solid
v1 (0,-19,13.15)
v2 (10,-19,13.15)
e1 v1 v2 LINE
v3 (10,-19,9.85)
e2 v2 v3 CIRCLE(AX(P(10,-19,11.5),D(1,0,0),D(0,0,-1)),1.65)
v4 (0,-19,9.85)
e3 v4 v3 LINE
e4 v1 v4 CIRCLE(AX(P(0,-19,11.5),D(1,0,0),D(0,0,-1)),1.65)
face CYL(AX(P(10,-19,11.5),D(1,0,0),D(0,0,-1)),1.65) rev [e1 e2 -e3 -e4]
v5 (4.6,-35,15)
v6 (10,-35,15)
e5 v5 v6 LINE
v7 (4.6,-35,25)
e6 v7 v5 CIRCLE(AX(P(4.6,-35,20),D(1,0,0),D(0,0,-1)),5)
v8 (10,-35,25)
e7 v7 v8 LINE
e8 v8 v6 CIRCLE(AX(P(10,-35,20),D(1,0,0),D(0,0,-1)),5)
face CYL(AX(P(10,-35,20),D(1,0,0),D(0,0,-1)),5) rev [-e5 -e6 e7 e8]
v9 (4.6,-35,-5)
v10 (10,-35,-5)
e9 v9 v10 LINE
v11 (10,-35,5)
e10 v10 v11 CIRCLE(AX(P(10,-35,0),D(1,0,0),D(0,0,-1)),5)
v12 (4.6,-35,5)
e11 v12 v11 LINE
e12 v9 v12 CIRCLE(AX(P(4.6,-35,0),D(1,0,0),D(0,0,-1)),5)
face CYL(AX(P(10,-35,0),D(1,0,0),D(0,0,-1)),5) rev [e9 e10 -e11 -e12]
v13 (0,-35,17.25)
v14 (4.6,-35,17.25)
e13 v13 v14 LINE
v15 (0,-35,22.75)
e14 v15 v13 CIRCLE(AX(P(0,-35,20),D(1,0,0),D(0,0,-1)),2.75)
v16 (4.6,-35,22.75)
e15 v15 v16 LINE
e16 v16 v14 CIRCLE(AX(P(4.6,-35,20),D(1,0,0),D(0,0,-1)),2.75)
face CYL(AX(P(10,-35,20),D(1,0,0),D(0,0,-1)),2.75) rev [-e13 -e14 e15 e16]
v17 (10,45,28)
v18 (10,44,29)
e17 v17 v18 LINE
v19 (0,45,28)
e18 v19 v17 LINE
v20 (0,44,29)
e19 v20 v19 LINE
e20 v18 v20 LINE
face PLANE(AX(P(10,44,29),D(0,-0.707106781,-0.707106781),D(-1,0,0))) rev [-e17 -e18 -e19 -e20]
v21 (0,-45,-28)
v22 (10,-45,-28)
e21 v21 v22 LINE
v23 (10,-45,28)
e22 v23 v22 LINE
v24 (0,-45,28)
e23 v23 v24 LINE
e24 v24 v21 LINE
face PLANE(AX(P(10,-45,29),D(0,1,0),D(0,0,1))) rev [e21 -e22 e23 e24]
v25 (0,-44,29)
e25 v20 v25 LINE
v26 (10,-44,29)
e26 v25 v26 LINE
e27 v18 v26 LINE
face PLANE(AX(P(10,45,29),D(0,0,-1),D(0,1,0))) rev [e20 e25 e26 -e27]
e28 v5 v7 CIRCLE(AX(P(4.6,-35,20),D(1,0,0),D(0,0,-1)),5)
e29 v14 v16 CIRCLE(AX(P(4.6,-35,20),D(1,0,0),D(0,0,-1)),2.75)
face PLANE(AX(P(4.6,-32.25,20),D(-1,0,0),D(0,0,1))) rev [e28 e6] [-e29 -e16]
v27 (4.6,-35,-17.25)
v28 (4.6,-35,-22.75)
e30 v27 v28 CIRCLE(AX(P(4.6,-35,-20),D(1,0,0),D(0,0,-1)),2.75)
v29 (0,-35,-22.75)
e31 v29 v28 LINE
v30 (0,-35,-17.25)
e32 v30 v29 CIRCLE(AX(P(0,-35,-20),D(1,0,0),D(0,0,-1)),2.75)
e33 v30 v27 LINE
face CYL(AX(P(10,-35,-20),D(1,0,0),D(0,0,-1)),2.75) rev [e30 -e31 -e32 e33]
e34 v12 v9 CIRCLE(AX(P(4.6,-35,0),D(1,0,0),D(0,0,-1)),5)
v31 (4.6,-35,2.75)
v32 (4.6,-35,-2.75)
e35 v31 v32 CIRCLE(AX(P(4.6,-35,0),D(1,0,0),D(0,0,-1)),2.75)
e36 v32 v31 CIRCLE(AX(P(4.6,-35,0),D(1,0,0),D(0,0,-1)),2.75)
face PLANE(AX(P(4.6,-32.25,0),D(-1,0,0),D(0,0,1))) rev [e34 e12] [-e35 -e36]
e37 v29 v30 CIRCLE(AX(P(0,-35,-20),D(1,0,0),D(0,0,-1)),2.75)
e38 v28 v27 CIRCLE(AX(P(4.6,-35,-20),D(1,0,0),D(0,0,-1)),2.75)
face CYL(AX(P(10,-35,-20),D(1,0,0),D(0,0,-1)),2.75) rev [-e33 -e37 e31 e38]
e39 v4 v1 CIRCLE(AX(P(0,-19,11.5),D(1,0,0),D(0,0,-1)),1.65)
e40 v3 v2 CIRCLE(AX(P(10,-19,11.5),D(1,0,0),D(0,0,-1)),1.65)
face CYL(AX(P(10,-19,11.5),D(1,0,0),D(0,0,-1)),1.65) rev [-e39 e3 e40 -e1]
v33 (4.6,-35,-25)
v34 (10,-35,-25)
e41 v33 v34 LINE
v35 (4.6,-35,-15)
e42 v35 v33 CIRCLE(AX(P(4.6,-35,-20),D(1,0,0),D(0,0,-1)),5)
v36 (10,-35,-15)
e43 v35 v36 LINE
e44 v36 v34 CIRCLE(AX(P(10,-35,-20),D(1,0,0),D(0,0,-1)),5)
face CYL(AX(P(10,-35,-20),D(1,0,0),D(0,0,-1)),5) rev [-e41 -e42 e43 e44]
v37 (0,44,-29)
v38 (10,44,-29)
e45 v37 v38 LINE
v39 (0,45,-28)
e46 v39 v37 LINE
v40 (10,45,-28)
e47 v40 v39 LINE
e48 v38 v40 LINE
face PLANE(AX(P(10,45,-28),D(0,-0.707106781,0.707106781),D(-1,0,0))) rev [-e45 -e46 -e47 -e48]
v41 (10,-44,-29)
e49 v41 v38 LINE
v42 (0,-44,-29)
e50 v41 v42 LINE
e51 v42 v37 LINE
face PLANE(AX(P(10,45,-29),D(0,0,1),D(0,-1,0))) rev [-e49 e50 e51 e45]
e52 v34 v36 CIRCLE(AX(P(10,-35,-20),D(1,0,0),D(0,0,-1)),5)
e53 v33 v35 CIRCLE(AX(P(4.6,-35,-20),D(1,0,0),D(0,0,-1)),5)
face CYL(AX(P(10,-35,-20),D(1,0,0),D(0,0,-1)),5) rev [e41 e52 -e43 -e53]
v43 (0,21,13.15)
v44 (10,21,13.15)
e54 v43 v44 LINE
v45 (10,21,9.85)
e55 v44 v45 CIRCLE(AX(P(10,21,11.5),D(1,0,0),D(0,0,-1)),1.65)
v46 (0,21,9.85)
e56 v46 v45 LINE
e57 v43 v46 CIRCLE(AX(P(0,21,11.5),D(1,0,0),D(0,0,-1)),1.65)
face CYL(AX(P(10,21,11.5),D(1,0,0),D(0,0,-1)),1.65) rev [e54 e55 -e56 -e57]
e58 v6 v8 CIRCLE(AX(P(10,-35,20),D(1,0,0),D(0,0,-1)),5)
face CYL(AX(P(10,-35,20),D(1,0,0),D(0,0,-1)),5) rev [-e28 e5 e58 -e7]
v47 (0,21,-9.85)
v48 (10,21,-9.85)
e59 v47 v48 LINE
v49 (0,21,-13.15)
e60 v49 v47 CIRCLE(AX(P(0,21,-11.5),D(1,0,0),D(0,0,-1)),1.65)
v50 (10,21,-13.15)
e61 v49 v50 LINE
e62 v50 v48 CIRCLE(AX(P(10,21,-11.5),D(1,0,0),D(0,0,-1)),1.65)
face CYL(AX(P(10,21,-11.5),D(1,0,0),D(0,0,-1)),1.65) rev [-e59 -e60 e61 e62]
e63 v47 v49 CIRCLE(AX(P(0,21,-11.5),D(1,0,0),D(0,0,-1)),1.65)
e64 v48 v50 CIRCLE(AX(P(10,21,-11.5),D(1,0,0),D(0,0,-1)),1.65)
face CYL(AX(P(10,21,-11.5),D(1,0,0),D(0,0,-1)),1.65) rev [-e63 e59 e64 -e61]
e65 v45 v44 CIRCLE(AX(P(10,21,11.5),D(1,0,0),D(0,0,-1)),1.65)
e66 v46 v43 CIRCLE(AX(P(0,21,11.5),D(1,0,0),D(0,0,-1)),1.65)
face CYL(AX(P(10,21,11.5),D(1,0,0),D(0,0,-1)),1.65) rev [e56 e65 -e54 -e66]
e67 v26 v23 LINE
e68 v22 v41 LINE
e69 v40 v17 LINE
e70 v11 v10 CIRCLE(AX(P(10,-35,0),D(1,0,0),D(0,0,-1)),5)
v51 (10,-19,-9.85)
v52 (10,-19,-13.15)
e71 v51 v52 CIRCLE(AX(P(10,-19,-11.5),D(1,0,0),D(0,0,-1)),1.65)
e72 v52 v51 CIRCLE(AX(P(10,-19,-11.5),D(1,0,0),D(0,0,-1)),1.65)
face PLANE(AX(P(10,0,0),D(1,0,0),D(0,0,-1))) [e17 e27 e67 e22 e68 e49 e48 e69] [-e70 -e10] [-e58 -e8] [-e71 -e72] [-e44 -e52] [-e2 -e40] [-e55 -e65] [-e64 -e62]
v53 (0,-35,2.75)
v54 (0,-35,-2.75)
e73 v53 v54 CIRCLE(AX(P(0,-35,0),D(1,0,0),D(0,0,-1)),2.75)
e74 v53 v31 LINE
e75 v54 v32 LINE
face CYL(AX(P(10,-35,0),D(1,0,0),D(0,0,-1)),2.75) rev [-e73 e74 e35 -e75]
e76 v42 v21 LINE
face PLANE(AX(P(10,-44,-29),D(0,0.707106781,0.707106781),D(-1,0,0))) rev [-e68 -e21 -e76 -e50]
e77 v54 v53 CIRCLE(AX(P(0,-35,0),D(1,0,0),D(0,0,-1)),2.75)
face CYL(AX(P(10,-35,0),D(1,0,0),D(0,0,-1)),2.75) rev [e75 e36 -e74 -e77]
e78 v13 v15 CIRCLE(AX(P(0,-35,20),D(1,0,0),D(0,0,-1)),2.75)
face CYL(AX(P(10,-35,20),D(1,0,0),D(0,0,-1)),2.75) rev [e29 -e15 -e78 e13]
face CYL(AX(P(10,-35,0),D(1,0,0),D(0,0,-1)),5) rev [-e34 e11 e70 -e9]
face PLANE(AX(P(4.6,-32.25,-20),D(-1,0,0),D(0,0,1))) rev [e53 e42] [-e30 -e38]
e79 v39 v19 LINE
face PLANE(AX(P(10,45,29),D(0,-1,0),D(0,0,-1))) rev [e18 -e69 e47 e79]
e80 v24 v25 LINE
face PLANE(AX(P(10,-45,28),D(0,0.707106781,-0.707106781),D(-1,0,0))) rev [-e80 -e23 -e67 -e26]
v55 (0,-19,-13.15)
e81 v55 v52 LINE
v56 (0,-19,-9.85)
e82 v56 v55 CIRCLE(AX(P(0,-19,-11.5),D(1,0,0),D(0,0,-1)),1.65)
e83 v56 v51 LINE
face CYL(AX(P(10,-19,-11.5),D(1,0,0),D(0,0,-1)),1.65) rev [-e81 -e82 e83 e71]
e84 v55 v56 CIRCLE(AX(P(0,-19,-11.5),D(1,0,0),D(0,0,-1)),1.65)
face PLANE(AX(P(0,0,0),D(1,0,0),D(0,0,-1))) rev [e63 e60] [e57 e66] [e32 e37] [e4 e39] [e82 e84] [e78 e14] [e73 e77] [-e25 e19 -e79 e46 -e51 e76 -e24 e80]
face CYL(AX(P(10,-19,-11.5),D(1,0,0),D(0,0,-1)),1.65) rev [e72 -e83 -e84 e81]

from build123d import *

# Parameters (mm, degrees)
SKETCH_1_W                   = 58
SKETCH_1_H                   = 90
EXTRUDE_1_DEPTH              = 10
HOLE_WIZARD_M4_1_D           = 3.3
HOLE_WIZARD_M5_1_D           = 5.5
HOLE_WIZARD_M5_1_CBORE_D     = 10
HOLE_WIZARD_M5_1_CBORE_DEPTH = 5.4
CHAMFER_1_SIZE               = 1


with BuildPart() as part:
    # 草图1 → 凸台-拉伸1 (new body)
    with BuildSketch(Plane(origin=(0, 0, 0), x_dir=(0, 0, -1), z_dir=(1, 0, 0))):
        Rectangle(SKETCH_1_W, SKETCH_1_H)
    extrude(amount=EXTRUDE_1_DEPTH)

    # M4 螺纹孔1 (through all)
    with Locations(Plane(origin=(10, 0, 0), x_dir=(0, 0, -1), z_dir=(1, 0, 0))):
        with Locations((-11.5, 21), (11.5, 21), (-11.5, -19), (11.5, -19)):
            Hole(HOLE_WIZARD_M4_1_D / 2)

    # M5 六角凹头螺钉的柱形沉头孔1 (through all)
    with Locations(Plane(origin=(10, 0, 0), x_dir=(0, 0, -1), z_dir=(1, 0, 0))):
        with Locations((-20, -35), (0, -35), (20, -35)):
            CounterBoreHole(HOLE_WIZARD_M5_1_D / 2, HOLE_WIZARD_M5_1_CBORE_D / 2, HOLE_WIZARD_M5_1_CBORE_DEPTH)

    # 倒角1
    chamfer_1_edges = [part.edges().sort_by_distance(p)[0] for p in [
        (5, -45, -29),
        (5, -45, 29),
        (5, 45, 29),
        (5, 45, -29),
    ]]
    chamfer(chamfer_1_edges, length=CHAMFER_1_SIZE)


solid = part.part
